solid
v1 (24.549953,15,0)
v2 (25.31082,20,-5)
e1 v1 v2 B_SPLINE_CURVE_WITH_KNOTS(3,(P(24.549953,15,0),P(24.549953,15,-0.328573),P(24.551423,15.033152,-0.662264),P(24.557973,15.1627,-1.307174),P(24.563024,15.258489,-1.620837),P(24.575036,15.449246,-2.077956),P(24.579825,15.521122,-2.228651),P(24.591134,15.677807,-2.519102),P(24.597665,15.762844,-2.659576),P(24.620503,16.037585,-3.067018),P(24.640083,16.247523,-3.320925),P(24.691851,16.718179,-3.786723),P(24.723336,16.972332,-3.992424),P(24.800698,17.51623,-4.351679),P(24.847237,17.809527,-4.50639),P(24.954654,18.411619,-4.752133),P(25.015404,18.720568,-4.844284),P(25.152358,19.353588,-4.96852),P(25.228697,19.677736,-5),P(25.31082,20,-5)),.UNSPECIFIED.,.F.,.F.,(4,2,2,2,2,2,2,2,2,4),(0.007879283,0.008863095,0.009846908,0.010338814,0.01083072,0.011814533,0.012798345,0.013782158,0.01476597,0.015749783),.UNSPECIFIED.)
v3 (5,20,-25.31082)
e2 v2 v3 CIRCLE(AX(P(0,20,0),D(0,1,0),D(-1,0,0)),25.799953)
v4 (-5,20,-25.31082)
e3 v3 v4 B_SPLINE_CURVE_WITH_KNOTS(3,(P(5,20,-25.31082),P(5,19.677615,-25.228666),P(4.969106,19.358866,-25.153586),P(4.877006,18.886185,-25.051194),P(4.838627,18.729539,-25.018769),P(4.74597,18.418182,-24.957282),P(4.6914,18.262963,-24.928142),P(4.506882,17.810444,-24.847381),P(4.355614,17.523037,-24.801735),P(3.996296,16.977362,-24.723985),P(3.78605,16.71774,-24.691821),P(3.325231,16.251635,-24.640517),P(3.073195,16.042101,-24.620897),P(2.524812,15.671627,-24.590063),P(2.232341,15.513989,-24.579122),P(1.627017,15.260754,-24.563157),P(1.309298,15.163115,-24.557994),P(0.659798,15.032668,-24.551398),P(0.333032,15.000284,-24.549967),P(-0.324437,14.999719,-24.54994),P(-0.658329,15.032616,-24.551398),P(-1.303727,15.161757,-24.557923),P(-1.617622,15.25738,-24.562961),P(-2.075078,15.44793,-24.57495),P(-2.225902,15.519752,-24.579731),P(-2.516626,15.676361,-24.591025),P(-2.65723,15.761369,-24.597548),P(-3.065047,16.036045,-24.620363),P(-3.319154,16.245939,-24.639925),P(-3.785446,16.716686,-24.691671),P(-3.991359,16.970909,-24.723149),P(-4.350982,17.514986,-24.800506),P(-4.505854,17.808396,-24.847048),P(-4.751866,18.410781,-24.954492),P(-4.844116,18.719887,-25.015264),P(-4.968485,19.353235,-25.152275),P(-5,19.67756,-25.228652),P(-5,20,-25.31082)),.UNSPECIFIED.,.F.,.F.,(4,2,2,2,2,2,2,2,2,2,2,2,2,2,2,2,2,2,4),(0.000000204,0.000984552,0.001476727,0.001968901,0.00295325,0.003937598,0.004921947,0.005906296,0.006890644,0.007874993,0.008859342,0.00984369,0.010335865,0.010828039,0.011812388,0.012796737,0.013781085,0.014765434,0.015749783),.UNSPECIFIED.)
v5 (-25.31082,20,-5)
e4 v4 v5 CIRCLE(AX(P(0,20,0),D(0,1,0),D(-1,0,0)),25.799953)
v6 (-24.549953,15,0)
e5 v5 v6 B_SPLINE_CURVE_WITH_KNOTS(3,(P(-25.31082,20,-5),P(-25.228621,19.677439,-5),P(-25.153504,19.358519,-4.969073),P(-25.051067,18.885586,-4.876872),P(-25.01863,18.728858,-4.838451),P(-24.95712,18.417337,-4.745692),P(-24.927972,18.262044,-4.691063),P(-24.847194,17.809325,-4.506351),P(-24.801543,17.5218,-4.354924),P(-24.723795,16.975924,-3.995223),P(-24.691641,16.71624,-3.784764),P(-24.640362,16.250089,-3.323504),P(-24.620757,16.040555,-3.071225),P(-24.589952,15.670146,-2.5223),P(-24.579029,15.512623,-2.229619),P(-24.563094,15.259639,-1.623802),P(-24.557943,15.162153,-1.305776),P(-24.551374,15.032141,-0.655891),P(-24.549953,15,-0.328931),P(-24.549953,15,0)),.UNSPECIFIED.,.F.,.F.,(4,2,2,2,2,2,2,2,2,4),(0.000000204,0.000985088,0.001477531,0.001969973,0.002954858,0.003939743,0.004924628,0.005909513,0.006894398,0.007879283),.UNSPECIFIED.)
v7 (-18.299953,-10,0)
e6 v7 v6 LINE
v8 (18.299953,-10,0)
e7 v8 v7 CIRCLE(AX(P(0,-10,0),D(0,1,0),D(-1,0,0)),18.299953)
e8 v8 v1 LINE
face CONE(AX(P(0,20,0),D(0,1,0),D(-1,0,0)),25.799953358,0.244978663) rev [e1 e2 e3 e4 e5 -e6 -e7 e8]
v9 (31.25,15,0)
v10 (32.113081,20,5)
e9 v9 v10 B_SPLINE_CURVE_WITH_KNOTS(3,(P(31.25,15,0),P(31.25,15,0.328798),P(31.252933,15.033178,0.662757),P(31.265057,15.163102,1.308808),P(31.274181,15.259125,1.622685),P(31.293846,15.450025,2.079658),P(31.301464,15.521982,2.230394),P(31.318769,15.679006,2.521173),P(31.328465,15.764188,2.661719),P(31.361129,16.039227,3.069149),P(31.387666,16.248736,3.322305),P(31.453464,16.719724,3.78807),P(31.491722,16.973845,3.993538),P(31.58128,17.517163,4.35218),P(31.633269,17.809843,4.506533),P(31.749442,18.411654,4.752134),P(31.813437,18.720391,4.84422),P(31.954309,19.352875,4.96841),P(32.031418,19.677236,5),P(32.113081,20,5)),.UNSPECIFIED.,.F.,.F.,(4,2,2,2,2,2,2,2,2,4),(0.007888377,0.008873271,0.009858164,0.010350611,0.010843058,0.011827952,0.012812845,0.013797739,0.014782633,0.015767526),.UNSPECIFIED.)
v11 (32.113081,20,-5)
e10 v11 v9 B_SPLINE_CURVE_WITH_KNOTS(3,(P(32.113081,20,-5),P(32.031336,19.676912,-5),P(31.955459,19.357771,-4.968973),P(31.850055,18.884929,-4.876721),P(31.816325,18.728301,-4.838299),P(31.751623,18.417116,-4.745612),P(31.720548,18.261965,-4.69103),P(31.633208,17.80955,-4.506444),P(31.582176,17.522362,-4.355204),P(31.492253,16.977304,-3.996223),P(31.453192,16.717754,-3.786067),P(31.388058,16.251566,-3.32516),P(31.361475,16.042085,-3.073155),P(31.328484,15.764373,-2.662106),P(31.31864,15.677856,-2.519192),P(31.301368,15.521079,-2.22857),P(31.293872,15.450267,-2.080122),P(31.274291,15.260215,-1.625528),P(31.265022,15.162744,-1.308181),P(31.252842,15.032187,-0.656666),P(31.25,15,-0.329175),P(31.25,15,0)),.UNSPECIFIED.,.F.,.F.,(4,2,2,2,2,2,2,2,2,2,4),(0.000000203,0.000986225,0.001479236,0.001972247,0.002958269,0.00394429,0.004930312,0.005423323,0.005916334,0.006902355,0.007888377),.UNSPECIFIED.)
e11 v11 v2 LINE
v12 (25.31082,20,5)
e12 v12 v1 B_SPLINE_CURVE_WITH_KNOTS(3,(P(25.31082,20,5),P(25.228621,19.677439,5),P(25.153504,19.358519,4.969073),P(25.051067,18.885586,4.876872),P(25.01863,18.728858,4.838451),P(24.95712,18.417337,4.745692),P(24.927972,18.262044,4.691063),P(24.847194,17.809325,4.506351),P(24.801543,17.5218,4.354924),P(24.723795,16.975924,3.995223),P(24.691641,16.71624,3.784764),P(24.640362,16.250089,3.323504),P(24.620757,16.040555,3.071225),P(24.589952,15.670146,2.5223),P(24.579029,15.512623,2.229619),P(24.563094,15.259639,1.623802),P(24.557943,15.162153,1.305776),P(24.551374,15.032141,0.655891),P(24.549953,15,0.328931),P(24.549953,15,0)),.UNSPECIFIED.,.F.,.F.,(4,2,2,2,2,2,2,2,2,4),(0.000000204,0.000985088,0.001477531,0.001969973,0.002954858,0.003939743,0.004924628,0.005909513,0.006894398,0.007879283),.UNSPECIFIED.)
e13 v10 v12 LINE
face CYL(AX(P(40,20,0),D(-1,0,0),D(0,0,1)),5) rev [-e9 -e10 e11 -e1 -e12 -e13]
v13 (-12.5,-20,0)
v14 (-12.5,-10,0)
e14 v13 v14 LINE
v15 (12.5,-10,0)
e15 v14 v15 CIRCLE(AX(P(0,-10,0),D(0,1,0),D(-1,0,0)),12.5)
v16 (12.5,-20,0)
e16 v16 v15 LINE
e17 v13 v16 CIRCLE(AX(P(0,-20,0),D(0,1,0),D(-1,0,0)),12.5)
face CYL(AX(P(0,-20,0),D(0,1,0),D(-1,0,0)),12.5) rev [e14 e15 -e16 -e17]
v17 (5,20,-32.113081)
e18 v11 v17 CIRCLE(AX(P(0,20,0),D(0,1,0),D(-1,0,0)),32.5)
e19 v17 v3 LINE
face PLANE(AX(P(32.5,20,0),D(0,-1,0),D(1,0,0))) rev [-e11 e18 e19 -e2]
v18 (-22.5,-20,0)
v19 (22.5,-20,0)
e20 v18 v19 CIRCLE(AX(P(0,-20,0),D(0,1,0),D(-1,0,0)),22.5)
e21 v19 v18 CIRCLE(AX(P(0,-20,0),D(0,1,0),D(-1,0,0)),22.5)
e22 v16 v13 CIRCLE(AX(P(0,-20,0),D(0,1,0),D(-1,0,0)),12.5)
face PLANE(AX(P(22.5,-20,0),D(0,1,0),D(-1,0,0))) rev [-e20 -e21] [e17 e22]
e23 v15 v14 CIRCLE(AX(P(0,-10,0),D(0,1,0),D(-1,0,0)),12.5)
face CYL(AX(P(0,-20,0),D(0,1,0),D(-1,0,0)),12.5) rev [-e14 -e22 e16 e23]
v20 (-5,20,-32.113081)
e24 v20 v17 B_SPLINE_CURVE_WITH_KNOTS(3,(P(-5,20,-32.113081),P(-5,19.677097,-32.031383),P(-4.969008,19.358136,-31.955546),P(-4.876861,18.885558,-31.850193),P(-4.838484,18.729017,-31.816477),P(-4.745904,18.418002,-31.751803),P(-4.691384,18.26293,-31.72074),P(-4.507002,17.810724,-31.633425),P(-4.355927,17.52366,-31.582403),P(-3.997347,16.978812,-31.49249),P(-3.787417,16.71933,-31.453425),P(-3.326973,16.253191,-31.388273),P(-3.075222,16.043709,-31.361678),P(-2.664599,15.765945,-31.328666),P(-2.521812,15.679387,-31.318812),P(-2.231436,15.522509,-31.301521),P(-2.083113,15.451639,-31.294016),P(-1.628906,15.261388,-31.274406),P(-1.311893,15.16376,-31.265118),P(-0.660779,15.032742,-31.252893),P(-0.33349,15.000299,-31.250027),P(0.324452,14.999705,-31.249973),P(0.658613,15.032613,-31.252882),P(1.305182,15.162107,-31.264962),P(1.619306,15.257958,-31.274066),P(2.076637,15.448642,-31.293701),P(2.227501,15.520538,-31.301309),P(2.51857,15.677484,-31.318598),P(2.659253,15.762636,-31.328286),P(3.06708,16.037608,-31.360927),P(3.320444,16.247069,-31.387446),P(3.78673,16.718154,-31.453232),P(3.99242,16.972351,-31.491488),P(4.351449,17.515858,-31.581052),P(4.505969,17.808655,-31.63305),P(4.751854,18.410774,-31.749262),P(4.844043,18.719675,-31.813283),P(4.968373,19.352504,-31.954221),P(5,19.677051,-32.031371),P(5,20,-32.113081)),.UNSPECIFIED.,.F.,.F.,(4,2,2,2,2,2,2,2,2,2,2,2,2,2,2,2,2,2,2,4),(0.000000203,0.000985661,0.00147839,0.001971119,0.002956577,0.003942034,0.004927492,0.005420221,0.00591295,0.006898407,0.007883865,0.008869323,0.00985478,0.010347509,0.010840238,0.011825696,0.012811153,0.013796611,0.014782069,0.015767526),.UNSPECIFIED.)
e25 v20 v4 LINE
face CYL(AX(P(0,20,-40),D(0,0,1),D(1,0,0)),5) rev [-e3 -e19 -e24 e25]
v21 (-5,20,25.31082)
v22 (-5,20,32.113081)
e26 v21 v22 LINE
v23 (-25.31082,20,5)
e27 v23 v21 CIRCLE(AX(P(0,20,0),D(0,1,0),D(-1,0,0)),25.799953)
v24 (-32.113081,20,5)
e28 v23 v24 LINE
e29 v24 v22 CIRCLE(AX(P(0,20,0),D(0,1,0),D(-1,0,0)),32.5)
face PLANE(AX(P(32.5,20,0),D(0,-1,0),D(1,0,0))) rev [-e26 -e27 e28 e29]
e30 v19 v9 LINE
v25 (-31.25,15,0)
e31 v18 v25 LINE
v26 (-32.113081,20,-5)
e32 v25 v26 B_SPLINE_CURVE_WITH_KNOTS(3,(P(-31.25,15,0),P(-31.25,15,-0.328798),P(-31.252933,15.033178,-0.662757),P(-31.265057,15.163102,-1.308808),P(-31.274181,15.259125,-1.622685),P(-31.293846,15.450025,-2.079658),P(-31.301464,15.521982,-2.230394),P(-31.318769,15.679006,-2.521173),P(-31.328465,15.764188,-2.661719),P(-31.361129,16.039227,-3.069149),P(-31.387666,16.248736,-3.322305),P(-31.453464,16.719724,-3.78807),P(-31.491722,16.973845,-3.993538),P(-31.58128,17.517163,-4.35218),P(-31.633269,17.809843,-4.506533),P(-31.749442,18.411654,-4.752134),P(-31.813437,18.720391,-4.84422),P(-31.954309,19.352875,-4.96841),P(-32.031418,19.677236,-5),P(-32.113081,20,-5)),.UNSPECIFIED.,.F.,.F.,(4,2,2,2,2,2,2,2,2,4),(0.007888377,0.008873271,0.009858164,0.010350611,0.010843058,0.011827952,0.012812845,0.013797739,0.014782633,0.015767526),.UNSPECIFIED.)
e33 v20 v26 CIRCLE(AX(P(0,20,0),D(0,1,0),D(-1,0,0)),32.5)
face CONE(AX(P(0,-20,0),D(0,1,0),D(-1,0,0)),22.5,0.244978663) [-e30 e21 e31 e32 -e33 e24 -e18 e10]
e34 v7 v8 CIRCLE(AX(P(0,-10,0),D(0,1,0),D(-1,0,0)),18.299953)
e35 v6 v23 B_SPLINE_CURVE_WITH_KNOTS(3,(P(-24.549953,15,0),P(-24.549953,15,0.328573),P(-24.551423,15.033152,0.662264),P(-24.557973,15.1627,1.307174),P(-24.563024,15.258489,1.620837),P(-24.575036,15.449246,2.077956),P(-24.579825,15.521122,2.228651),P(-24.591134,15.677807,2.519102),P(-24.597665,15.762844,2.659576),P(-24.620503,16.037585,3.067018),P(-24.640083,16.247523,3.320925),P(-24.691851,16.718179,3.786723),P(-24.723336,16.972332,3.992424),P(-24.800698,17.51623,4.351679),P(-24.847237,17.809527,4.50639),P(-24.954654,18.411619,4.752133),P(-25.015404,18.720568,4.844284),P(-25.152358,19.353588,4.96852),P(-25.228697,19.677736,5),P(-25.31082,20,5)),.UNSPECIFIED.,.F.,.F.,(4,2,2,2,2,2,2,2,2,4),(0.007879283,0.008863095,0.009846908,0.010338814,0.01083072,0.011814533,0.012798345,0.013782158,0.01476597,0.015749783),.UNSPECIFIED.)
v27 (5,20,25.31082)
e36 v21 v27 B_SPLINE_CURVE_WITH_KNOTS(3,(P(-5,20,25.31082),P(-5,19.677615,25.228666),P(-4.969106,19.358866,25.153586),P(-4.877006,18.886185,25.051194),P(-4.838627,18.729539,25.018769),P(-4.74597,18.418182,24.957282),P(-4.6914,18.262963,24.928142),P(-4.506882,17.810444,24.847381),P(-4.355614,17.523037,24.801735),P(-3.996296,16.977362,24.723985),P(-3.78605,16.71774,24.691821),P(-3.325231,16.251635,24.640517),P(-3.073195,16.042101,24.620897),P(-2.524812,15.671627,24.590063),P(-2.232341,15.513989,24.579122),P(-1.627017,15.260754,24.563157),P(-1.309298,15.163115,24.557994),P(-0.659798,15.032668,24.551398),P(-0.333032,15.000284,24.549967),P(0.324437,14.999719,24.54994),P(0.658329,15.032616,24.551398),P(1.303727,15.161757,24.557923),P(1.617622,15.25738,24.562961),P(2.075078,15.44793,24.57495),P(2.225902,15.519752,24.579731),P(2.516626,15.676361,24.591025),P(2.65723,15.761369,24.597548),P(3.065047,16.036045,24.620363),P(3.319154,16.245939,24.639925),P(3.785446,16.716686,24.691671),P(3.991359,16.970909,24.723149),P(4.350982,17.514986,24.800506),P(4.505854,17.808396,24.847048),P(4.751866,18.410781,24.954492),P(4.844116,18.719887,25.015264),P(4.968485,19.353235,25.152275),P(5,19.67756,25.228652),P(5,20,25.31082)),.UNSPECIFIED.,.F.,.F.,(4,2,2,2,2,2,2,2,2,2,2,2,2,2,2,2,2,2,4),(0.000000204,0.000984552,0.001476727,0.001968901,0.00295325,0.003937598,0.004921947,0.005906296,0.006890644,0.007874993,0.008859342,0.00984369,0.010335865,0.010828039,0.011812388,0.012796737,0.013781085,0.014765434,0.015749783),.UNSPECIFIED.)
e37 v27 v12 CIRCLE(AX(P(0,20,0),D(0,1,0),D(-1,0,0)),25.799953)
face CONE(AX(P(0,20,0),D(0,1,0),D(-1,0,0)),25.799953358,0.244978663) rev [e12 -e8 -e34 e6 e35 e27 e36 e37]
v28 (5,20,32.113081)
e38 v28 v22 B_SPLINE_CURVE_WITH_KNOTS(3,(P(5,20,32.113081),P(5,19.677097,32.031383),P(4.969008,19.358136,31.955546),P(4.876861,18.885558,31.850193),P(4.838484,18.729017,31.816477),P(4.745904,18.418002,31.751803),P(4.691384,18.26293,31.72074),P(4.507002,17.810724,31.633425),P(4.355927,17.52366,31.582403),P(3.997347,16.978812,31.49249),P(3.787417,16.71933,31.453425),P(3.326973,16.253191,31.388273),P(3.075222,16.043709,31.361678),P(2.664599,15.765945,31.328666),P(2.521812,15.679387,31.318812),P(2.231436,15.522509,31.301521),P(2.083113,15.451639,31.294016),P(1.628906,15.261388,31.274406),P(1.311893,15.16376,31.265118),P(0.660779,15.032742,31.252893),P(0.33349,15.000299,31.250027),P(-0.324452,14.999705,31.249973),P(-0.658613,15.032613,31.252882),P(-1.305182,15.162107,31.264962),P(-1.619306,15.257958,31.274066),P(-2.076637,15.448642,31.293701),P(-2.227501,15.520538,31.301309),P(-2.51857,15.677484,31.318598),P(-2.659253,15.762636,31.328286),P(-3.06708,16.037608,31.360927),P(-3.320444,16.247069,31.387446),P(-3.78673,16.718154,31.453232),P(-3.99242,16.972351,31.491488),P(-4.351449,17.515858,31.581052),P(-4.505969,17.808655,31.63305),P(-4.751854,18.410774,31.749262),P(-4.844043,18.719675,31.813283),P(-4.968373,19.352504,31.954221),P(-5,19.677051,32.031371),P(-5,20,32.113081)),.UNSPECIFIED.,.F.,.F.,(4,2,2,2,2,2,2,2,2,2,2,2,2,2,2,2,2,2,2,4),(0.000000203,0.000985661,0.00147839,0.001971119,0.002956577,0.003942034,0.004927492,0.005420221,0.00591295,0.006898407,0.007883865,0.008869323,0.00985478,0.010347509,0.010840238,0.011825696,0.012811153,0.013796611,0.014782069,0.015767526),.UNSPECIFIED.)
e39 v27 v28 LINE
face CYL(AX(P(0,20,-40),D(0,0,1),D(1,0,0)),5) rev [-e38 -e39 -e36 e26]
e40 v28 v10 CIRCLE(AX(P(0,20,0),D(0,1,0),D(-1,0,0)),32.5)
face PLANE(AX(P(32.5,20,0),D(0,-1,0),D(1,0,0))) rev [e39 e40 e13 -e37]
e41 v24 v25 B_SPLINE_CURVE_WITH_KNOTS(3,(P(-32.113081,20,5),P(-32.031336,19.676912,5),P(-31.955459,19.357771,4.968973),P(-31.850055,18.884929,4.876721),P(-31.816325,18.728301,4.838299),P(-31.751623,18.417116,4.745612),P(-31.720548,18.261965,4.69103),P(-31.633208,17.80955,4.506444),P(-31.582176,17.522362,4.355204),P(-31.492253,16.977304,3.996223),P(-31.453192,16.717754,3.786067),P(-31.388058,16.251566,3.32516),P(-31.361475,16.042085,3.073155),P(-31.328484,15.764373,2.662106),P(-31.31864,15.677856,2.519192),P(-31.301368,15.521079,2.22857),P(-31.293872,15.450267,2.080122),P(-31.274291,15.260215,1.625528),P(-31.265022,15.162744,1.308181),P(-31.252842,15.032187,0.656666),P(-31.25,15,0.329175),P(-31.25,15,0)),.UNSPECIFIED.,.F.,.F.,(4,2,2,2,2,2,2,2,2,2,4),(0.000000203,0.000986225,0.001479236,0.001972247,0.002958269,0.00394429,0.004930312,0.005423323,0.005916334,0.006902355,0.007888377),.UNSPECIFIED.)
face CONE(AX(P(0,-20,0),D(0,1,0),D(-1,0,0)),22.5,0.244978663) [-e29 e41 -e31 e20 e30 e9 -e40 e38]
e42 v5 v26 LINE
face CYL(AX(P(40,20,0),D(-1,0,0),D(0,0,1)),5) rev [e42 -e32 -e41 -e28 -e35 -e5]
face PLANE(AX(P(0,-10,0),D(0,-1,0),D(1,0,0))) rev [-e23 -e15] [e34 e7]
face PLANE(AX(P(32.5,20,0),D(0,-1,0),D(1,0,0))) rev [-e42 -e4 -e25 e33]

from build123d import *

# Parameters (mm, degrees)
SKETCH2_R          = 12.5
CUT_EXTRUDE1_DEPTH = 10
CUT_EXTRUDE2_DEPTH = 40
CIRPATTERN1_COUNT  = 4


with BuildPart() as part:
    # Sketch1 → Revolve1 (revolve)
    with BuildSketch(Plane.XY, mode=Mode.PRIVATE) as revolve1_sk:
        Polygon((32.5, 20), (22.5, -20), (0, -20), (0, -10), (18.299953358, -10), (25.799953358, 20), align=None)
    revolve(revolve1_sk.sketch.rotate(Axis((0, 20, 0), (0, -1, 0)), 180), axis=Axis((0, 20, 0), (0, -1, 0)))

    # Sketch2 → Cut-Extrude1 (cut)
    with BuildSketch(Plane(origin=(0, -10, 0), x_dir=(1, 0, 0), z_dir=(0, 1, 0))):
        with Locations(Location((0, 0, 0), (0, 0, 180))):
            Circle(SKETCH2_R)
    extrude(amount=-CUT_EXTRUDE1_DEPTH, mode=Mode.SUBTRACT)

    # Sketch4 → Cut-Extrude2 (cut, symmetric)
    with BuildSketch(Plane.XY):
        with BuildLine():
            Line((-5, 20), (5, 20))
            ThreePointArc((5, 20), (0, 15), (-5, 20))
        make_face()
    cut_extrude2 = extrude(amount=CUT_EXTRUDE2_DEPTH, both=True, mode=Mode.SUBTRACT)

    # CirPattern1: Cut-Extrude2 ×4 about axis
    cirpattern1_axis = Axis((0, -20, 0), (0, 1, 0))
    for i in range(1, CIRPATTERN1_COUNT):
        add(cut_extrude2.rotate(cirpattern1_axis, i * 360 / CIRPATTERN1_COUNT), mode=Mode.SUBTRACT)


solid = part.part
